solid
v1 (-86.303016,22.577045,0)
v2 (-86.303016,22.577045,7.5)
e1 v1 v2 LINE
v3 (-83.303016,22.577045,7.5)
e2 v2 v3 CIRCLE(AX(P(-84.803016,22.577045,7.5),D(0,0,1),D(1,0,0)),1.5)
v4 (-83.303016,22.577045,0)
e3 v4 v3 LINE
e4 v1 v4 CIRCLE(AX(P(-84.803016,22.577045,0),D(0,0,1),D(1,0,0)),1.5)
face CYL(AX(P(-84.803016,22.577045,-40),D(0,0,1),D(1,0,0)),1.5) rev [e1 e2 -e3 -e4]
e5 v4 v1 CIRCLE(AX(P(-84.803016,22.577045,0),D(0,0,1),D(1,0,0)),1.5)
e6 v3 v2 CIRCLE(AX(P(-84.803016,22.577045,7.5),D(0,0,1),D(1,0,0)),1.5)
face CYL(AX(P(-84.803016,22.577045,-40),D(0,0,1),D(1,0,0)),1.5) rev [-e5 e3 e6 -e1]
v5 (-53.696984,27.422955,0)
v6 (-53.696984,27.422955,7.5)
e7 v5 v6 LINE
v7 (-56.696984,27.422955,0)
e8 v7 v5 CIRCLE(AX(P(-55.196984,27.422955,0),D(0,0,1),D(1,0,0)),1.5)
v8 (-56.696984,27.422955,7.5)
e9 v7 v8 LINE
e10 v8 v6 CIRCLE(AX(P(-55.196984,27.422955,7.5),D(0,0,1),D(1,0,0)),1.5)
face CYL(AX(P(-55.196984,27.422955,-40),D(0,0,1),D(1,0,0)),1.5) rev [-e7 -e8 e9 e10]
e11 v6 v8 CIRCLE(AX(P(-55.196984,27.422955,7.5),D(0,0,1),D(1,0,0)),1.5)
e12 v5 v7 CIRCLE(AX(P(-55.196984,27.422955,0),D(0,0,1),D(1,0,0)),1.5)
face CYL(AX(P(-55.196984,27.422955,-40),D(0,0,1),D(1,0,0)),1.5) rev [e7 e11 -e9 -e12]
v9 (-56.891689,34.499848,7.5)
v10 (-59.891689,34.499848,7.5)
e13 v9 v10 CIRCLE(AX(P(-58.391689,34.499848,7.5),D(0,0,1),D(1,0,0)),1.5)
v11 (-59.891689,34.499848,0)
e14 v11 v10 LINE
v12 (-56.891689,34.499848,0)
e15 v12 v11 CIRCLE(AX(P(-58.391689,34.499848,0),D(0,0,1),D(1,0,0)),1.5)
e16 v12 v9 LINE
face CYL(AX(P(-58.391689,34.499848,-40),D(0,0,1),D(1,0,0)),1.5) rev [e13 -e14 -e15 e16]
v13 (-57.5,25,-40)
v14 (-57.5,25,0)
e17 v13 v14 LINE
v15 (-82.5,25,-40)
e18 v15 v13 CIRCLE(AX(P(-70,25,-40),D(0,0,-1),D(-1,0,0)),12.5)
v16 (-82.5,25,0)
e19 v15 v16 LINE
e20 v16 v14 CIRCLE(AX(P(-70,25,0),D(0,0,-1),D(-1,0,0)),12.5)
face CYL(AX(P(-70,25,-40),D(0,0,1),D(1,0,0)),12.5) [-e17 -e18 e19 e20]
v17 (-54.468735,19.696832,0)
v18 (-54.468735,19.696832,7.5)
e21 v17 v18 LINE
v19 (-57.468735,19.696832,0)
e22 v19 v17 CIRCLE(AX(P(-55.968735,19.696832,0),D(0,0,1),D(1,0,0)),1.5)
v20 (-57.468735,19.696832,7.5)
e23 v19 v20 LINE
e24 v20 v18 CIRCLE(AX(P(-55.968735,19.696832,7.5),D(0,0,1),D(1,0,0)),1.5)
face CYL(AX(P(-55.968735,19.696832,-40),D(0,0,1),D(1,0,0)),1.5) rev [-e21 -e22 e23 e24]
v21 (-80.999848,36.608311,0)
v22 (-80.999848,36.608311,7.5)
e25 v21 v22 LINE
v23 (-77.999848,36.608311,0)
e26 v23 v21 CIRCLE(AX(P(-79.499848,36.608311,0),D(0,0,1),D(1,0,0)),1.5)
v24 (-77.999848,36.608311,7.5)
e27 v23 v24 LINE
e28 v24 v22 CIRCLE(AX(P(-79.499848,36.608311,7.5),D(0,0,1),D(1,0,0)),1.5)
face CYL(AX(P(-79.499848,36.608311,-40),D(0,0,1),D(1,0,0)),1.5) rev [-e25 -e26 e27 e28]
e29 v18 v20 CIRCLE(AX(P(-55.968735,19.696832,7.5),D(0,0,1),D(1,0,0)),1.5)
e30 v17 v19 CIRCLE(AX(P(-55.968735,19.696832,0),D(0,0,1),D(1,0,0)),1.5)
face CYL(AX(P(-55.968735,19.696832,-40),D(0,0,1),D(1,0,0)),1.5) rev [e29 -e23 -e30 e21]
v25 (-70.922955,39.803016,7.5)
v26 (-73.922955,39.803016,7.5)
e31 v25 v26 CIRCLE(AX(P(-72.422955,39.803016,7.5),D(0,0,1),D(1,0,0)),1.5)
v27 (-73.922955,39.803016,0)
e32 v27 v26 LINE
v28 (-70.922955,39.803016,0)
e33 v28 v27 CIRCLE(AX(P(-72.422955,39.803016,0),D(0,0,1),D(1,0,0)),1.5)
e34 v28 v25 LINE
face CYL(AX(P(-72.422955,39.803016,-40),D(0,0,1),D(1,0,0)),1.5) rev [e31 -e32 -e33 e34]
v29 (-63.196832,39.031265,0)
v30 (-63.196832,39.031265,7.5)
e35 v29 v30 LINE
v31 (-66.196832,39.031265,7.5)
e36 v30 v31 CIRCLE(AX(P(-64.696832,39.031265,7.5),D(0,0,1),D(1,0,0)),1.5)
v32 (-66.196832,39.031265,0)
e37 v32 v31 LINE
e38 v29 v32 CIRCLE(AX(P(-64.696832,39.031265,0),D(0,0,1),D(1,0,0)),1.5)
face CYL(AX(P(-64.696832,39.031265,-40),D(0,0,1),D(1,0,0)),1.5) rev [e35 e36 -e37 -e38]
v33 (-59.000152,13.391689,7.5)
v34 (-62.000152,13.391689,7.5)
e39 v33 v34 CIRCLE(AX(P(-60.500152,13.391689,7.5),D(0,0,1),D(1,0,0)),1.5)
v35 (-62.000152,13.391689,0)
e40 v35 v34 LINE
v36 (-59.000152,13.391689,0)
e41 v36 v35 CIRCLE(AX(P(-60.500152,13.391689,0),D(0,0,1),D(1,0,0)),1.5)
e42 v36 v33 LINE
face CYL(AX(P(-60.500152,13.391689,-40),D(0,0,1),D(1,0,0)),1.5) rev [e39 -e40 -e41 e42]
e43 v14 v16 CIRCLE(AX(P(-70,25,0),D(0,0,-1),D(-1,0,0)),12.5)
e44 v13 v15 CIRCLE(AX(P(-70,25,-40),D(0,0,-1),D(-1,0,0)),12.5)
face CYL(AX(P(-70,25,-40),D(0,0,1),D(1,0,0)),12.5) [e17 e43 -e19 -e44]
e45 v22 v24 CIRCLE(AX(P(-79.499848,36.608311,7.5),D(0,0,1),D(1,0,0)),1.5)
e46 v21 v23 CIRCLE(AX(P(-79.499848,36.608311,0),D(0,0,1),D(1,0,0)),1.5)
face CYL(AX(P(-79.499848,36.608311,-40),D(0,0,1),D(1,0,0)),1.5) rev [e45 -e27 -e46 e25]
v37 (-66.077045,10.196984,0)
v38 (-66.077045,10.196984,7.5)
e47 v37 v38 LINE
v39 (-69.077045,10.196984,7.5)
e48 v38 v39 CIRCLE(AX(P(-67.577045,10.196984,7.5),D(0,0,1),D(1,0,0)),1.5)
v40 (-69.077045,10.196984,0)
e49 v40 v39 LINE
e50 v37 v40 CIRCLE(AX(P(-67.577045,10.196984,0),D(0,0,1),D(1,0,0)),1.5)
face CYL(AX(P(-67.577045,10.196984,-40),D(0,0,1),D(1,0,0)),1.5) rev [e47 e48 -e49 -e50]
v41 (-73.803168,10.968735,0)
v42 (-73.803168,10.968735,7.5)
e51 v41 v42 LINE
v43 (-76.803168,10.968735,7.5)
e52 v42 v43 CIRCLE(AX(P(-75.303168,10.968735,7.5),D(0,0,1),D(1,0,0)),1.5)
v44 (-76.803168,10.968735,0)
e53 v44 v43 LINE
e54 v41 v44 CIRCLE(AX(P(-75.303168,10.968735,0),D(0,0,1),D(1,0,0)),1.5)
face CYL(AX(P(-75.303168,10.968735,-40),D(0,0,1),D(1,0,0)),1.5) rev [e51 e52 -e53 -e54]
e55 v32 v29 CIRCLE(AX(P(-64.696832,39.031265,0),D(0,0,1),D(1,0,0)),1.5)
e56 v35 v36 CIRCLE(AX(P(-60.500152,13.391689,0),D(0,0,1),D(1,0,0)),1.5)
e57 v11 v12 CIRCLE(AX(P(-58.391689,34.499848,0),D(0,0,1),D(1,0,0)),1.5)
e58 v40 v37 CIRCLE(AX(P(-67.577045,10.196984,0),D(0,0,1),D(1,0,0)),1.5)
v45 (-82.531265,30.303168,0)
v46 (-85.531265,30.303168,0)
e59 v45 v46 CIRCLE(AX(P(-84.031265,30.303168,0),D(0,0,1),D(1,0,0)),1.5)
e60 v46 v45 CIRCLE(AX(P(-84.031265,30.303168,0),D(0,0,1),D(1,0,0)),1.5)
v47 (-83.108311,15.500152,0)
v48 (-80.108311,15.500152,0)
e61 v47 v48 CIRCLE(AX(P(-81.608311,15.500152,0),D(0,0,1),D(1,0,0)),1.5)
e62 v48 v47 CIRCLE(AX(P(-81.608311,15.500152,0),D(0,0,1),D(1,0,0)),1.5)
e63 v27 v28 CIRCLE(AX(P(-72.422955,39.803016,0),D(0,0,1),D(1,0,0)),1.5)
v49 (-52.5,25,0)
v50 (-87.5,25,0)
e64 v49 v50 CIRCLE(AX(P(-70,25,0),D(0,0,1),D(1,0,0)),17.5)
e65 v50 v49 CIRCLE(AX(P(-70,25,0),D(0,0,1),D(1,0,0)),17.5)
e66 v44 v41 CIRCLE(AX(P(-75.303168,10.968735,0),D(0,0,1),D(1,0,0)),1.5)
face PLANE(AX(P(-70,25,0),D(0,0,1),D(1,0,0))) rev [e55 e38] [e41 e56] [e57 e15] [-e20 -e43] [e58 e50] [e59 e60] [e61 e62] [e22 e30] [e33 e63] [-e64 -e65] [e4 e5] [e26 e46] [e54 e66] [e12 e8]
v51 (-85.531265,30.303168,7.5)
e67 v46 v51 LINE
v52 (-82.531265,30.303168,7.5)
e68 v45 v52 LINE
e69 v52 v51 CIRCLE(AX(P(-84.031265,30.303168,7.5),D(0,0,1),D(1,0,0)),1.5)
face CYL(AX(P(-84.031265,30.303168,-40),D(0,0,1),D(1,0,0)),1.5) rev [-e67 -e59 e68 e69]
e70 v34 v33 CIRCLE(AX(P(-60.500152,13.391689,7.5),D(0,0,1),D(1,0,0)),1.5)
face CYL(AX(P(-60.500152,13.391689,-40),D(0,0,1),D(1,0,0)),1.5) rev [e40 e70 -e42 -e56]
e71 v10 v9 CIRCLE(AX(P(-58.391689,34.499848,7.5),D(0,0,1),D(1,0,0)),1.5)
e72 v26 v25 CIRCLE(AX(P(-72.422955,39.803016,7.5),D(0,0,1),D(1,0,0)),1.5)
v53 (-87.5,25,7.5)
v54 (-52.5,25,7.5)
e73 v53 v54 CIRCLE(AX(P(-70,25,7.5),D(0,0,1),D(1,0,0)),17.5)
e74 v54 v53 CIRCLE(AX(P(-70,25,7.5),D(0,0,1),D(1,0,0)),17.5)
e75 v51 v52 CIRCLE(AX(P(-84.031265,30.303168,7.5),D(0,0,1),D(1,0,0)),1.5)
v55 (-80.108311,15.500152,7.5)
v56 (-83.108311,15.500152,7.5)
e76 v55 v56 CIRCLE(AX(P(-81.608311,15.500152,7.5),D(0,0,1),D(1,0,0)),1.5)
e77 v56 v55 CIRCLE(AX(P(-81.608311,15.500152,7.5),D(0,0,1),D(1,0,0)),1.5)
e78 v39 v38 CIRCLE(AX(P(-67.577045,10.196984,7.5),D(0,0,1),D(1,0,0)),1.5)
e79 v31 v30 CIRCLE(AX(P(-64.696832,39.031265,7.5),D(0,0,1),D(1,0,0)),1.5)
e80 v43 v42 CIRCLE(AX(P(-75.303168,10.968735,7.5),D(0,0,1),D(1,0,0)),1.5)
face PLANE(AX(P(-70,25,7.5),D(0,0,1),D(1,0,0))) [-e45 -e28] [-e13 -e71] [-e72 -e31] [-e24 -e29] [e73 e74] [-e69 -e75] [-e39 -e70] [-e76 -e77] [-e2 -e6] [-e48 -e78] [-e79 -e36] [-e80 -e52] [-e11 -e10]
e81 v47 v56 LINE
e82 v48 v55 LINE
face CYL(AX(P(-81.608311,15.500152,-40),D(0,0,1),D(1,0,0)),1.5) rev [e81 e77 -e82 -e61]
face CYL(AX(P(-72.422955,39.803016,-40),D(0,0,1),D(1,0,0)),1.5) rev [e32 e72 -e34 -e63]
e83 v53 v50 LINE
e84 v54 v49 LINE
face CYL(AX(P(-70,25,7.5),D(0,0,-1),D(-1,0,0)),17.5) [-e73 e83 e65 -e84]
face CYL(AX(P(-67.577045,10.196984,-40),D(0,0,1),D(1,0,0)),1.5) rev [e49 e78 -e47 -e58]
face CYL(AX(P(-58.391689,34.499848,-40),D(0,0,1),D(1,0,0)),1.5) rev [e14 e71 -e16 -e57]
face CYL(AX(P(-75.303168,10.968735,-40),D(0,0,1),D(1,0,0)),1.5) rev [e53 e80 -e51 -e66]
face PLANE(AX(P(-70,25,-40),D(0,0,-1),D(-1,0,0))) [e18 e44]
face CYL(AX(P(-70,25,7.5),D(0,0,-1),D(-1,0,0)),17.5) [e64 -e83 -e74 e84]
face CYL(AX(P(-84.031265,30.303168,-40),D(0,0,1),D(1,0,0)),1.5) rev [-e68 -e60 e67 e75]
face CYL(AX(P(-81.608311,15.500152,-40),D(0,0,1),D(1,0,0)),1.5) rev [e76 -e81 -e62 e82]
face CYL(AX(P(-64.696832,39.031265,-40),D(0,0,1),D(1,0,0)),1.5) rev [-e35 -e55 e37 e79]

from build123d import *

# Parameters (mm, degrees)
SKETCH1_R               = 17.5
BOSS_EXTRUDE1_DEPTH     = 7.5
SKETCH2_R               = 12.5
BOSS_EXTRUDE2_DEPTH     = 40
CUT_EXTRUDE1_DEPTH      = 109.253175473
CUT_EXTRUDE1_DEPTH_BACK = 109.253175473
SKETCH3_R               = 1.5


with BuildPart() as part:
    # Sketch1 → Boss-Extrude1 (new body)
    with BuildSketch(Plane.XY):
        with Locations((-70, 25)):
            Circle(SKETCH1_R)
    extrude(amount=BOSS_EXTRUDE1_DEPTH)

    # Sketch2 → Boss-Extrude2 (add)
    with BuildSketch(Plane(origin=(0, 0, 0), x_dir=(-1, 0, 0), z_dir=(0, 0, -1))):
        with Locations((70, 25)):
            Circle(SKETCH2_R)
    extrude(amount=BOSS_EXTRUDE2_DEPTH)

    # Sketch3 → Cut-Extrude1 (cut, two sides: drawn at the far end of the back side and taken through both)
    with BuildSketch(Plane.XY.offset(7.5).offset(-CUT_EXTRUDE1_DEPTH_BACK)):
        with Locations((-81.608310906, 15.50015169)):
            Circle(SKETCH3_R)
        with Locations((-84.803016294, 22.577045484)):
            Circle(SKETCH3_R)
        with Locations((-84.031265422, 30.303167984)):
            Circle(SKETCH3_R)
        with Locations((-79.49984831, 36.608310906)):
            Circle(SKETCH3_R)
        with Locations((-72.422954516, 39.803016294)):
            Circle(SKETCH3_R)
        with Locations((-64.696832016, 39.031265422)):
            Circle(SKETCH3_R)
        with Locations((-58.391689094, 34.49984831)):
            Circle(SKETCH3_R)
        with Locations((-55.196983706, 27.422954516)):
            Circle(SKETCH3_R)
        with Locations((-55.968734578, 19.696832016)):
            Circle(SKETCH3_R)
        with Locations((-60.50015169, 13.391689094)):
            Circle(SKETCH3_R)
        with Locations((-67.577045484, 10.196983706)):
            Circle(SKETCH3_R)
        with Locations((-75.303167984, 10.968734578)):
            Circle(SKETCH3_R)
    extrude(amount=CUT_EXTRUDE1_DEPTH + CUT_EXTRUDE1_DEPTH_BACK, mode=Mode.SUBTRACT)


solid = part.part
